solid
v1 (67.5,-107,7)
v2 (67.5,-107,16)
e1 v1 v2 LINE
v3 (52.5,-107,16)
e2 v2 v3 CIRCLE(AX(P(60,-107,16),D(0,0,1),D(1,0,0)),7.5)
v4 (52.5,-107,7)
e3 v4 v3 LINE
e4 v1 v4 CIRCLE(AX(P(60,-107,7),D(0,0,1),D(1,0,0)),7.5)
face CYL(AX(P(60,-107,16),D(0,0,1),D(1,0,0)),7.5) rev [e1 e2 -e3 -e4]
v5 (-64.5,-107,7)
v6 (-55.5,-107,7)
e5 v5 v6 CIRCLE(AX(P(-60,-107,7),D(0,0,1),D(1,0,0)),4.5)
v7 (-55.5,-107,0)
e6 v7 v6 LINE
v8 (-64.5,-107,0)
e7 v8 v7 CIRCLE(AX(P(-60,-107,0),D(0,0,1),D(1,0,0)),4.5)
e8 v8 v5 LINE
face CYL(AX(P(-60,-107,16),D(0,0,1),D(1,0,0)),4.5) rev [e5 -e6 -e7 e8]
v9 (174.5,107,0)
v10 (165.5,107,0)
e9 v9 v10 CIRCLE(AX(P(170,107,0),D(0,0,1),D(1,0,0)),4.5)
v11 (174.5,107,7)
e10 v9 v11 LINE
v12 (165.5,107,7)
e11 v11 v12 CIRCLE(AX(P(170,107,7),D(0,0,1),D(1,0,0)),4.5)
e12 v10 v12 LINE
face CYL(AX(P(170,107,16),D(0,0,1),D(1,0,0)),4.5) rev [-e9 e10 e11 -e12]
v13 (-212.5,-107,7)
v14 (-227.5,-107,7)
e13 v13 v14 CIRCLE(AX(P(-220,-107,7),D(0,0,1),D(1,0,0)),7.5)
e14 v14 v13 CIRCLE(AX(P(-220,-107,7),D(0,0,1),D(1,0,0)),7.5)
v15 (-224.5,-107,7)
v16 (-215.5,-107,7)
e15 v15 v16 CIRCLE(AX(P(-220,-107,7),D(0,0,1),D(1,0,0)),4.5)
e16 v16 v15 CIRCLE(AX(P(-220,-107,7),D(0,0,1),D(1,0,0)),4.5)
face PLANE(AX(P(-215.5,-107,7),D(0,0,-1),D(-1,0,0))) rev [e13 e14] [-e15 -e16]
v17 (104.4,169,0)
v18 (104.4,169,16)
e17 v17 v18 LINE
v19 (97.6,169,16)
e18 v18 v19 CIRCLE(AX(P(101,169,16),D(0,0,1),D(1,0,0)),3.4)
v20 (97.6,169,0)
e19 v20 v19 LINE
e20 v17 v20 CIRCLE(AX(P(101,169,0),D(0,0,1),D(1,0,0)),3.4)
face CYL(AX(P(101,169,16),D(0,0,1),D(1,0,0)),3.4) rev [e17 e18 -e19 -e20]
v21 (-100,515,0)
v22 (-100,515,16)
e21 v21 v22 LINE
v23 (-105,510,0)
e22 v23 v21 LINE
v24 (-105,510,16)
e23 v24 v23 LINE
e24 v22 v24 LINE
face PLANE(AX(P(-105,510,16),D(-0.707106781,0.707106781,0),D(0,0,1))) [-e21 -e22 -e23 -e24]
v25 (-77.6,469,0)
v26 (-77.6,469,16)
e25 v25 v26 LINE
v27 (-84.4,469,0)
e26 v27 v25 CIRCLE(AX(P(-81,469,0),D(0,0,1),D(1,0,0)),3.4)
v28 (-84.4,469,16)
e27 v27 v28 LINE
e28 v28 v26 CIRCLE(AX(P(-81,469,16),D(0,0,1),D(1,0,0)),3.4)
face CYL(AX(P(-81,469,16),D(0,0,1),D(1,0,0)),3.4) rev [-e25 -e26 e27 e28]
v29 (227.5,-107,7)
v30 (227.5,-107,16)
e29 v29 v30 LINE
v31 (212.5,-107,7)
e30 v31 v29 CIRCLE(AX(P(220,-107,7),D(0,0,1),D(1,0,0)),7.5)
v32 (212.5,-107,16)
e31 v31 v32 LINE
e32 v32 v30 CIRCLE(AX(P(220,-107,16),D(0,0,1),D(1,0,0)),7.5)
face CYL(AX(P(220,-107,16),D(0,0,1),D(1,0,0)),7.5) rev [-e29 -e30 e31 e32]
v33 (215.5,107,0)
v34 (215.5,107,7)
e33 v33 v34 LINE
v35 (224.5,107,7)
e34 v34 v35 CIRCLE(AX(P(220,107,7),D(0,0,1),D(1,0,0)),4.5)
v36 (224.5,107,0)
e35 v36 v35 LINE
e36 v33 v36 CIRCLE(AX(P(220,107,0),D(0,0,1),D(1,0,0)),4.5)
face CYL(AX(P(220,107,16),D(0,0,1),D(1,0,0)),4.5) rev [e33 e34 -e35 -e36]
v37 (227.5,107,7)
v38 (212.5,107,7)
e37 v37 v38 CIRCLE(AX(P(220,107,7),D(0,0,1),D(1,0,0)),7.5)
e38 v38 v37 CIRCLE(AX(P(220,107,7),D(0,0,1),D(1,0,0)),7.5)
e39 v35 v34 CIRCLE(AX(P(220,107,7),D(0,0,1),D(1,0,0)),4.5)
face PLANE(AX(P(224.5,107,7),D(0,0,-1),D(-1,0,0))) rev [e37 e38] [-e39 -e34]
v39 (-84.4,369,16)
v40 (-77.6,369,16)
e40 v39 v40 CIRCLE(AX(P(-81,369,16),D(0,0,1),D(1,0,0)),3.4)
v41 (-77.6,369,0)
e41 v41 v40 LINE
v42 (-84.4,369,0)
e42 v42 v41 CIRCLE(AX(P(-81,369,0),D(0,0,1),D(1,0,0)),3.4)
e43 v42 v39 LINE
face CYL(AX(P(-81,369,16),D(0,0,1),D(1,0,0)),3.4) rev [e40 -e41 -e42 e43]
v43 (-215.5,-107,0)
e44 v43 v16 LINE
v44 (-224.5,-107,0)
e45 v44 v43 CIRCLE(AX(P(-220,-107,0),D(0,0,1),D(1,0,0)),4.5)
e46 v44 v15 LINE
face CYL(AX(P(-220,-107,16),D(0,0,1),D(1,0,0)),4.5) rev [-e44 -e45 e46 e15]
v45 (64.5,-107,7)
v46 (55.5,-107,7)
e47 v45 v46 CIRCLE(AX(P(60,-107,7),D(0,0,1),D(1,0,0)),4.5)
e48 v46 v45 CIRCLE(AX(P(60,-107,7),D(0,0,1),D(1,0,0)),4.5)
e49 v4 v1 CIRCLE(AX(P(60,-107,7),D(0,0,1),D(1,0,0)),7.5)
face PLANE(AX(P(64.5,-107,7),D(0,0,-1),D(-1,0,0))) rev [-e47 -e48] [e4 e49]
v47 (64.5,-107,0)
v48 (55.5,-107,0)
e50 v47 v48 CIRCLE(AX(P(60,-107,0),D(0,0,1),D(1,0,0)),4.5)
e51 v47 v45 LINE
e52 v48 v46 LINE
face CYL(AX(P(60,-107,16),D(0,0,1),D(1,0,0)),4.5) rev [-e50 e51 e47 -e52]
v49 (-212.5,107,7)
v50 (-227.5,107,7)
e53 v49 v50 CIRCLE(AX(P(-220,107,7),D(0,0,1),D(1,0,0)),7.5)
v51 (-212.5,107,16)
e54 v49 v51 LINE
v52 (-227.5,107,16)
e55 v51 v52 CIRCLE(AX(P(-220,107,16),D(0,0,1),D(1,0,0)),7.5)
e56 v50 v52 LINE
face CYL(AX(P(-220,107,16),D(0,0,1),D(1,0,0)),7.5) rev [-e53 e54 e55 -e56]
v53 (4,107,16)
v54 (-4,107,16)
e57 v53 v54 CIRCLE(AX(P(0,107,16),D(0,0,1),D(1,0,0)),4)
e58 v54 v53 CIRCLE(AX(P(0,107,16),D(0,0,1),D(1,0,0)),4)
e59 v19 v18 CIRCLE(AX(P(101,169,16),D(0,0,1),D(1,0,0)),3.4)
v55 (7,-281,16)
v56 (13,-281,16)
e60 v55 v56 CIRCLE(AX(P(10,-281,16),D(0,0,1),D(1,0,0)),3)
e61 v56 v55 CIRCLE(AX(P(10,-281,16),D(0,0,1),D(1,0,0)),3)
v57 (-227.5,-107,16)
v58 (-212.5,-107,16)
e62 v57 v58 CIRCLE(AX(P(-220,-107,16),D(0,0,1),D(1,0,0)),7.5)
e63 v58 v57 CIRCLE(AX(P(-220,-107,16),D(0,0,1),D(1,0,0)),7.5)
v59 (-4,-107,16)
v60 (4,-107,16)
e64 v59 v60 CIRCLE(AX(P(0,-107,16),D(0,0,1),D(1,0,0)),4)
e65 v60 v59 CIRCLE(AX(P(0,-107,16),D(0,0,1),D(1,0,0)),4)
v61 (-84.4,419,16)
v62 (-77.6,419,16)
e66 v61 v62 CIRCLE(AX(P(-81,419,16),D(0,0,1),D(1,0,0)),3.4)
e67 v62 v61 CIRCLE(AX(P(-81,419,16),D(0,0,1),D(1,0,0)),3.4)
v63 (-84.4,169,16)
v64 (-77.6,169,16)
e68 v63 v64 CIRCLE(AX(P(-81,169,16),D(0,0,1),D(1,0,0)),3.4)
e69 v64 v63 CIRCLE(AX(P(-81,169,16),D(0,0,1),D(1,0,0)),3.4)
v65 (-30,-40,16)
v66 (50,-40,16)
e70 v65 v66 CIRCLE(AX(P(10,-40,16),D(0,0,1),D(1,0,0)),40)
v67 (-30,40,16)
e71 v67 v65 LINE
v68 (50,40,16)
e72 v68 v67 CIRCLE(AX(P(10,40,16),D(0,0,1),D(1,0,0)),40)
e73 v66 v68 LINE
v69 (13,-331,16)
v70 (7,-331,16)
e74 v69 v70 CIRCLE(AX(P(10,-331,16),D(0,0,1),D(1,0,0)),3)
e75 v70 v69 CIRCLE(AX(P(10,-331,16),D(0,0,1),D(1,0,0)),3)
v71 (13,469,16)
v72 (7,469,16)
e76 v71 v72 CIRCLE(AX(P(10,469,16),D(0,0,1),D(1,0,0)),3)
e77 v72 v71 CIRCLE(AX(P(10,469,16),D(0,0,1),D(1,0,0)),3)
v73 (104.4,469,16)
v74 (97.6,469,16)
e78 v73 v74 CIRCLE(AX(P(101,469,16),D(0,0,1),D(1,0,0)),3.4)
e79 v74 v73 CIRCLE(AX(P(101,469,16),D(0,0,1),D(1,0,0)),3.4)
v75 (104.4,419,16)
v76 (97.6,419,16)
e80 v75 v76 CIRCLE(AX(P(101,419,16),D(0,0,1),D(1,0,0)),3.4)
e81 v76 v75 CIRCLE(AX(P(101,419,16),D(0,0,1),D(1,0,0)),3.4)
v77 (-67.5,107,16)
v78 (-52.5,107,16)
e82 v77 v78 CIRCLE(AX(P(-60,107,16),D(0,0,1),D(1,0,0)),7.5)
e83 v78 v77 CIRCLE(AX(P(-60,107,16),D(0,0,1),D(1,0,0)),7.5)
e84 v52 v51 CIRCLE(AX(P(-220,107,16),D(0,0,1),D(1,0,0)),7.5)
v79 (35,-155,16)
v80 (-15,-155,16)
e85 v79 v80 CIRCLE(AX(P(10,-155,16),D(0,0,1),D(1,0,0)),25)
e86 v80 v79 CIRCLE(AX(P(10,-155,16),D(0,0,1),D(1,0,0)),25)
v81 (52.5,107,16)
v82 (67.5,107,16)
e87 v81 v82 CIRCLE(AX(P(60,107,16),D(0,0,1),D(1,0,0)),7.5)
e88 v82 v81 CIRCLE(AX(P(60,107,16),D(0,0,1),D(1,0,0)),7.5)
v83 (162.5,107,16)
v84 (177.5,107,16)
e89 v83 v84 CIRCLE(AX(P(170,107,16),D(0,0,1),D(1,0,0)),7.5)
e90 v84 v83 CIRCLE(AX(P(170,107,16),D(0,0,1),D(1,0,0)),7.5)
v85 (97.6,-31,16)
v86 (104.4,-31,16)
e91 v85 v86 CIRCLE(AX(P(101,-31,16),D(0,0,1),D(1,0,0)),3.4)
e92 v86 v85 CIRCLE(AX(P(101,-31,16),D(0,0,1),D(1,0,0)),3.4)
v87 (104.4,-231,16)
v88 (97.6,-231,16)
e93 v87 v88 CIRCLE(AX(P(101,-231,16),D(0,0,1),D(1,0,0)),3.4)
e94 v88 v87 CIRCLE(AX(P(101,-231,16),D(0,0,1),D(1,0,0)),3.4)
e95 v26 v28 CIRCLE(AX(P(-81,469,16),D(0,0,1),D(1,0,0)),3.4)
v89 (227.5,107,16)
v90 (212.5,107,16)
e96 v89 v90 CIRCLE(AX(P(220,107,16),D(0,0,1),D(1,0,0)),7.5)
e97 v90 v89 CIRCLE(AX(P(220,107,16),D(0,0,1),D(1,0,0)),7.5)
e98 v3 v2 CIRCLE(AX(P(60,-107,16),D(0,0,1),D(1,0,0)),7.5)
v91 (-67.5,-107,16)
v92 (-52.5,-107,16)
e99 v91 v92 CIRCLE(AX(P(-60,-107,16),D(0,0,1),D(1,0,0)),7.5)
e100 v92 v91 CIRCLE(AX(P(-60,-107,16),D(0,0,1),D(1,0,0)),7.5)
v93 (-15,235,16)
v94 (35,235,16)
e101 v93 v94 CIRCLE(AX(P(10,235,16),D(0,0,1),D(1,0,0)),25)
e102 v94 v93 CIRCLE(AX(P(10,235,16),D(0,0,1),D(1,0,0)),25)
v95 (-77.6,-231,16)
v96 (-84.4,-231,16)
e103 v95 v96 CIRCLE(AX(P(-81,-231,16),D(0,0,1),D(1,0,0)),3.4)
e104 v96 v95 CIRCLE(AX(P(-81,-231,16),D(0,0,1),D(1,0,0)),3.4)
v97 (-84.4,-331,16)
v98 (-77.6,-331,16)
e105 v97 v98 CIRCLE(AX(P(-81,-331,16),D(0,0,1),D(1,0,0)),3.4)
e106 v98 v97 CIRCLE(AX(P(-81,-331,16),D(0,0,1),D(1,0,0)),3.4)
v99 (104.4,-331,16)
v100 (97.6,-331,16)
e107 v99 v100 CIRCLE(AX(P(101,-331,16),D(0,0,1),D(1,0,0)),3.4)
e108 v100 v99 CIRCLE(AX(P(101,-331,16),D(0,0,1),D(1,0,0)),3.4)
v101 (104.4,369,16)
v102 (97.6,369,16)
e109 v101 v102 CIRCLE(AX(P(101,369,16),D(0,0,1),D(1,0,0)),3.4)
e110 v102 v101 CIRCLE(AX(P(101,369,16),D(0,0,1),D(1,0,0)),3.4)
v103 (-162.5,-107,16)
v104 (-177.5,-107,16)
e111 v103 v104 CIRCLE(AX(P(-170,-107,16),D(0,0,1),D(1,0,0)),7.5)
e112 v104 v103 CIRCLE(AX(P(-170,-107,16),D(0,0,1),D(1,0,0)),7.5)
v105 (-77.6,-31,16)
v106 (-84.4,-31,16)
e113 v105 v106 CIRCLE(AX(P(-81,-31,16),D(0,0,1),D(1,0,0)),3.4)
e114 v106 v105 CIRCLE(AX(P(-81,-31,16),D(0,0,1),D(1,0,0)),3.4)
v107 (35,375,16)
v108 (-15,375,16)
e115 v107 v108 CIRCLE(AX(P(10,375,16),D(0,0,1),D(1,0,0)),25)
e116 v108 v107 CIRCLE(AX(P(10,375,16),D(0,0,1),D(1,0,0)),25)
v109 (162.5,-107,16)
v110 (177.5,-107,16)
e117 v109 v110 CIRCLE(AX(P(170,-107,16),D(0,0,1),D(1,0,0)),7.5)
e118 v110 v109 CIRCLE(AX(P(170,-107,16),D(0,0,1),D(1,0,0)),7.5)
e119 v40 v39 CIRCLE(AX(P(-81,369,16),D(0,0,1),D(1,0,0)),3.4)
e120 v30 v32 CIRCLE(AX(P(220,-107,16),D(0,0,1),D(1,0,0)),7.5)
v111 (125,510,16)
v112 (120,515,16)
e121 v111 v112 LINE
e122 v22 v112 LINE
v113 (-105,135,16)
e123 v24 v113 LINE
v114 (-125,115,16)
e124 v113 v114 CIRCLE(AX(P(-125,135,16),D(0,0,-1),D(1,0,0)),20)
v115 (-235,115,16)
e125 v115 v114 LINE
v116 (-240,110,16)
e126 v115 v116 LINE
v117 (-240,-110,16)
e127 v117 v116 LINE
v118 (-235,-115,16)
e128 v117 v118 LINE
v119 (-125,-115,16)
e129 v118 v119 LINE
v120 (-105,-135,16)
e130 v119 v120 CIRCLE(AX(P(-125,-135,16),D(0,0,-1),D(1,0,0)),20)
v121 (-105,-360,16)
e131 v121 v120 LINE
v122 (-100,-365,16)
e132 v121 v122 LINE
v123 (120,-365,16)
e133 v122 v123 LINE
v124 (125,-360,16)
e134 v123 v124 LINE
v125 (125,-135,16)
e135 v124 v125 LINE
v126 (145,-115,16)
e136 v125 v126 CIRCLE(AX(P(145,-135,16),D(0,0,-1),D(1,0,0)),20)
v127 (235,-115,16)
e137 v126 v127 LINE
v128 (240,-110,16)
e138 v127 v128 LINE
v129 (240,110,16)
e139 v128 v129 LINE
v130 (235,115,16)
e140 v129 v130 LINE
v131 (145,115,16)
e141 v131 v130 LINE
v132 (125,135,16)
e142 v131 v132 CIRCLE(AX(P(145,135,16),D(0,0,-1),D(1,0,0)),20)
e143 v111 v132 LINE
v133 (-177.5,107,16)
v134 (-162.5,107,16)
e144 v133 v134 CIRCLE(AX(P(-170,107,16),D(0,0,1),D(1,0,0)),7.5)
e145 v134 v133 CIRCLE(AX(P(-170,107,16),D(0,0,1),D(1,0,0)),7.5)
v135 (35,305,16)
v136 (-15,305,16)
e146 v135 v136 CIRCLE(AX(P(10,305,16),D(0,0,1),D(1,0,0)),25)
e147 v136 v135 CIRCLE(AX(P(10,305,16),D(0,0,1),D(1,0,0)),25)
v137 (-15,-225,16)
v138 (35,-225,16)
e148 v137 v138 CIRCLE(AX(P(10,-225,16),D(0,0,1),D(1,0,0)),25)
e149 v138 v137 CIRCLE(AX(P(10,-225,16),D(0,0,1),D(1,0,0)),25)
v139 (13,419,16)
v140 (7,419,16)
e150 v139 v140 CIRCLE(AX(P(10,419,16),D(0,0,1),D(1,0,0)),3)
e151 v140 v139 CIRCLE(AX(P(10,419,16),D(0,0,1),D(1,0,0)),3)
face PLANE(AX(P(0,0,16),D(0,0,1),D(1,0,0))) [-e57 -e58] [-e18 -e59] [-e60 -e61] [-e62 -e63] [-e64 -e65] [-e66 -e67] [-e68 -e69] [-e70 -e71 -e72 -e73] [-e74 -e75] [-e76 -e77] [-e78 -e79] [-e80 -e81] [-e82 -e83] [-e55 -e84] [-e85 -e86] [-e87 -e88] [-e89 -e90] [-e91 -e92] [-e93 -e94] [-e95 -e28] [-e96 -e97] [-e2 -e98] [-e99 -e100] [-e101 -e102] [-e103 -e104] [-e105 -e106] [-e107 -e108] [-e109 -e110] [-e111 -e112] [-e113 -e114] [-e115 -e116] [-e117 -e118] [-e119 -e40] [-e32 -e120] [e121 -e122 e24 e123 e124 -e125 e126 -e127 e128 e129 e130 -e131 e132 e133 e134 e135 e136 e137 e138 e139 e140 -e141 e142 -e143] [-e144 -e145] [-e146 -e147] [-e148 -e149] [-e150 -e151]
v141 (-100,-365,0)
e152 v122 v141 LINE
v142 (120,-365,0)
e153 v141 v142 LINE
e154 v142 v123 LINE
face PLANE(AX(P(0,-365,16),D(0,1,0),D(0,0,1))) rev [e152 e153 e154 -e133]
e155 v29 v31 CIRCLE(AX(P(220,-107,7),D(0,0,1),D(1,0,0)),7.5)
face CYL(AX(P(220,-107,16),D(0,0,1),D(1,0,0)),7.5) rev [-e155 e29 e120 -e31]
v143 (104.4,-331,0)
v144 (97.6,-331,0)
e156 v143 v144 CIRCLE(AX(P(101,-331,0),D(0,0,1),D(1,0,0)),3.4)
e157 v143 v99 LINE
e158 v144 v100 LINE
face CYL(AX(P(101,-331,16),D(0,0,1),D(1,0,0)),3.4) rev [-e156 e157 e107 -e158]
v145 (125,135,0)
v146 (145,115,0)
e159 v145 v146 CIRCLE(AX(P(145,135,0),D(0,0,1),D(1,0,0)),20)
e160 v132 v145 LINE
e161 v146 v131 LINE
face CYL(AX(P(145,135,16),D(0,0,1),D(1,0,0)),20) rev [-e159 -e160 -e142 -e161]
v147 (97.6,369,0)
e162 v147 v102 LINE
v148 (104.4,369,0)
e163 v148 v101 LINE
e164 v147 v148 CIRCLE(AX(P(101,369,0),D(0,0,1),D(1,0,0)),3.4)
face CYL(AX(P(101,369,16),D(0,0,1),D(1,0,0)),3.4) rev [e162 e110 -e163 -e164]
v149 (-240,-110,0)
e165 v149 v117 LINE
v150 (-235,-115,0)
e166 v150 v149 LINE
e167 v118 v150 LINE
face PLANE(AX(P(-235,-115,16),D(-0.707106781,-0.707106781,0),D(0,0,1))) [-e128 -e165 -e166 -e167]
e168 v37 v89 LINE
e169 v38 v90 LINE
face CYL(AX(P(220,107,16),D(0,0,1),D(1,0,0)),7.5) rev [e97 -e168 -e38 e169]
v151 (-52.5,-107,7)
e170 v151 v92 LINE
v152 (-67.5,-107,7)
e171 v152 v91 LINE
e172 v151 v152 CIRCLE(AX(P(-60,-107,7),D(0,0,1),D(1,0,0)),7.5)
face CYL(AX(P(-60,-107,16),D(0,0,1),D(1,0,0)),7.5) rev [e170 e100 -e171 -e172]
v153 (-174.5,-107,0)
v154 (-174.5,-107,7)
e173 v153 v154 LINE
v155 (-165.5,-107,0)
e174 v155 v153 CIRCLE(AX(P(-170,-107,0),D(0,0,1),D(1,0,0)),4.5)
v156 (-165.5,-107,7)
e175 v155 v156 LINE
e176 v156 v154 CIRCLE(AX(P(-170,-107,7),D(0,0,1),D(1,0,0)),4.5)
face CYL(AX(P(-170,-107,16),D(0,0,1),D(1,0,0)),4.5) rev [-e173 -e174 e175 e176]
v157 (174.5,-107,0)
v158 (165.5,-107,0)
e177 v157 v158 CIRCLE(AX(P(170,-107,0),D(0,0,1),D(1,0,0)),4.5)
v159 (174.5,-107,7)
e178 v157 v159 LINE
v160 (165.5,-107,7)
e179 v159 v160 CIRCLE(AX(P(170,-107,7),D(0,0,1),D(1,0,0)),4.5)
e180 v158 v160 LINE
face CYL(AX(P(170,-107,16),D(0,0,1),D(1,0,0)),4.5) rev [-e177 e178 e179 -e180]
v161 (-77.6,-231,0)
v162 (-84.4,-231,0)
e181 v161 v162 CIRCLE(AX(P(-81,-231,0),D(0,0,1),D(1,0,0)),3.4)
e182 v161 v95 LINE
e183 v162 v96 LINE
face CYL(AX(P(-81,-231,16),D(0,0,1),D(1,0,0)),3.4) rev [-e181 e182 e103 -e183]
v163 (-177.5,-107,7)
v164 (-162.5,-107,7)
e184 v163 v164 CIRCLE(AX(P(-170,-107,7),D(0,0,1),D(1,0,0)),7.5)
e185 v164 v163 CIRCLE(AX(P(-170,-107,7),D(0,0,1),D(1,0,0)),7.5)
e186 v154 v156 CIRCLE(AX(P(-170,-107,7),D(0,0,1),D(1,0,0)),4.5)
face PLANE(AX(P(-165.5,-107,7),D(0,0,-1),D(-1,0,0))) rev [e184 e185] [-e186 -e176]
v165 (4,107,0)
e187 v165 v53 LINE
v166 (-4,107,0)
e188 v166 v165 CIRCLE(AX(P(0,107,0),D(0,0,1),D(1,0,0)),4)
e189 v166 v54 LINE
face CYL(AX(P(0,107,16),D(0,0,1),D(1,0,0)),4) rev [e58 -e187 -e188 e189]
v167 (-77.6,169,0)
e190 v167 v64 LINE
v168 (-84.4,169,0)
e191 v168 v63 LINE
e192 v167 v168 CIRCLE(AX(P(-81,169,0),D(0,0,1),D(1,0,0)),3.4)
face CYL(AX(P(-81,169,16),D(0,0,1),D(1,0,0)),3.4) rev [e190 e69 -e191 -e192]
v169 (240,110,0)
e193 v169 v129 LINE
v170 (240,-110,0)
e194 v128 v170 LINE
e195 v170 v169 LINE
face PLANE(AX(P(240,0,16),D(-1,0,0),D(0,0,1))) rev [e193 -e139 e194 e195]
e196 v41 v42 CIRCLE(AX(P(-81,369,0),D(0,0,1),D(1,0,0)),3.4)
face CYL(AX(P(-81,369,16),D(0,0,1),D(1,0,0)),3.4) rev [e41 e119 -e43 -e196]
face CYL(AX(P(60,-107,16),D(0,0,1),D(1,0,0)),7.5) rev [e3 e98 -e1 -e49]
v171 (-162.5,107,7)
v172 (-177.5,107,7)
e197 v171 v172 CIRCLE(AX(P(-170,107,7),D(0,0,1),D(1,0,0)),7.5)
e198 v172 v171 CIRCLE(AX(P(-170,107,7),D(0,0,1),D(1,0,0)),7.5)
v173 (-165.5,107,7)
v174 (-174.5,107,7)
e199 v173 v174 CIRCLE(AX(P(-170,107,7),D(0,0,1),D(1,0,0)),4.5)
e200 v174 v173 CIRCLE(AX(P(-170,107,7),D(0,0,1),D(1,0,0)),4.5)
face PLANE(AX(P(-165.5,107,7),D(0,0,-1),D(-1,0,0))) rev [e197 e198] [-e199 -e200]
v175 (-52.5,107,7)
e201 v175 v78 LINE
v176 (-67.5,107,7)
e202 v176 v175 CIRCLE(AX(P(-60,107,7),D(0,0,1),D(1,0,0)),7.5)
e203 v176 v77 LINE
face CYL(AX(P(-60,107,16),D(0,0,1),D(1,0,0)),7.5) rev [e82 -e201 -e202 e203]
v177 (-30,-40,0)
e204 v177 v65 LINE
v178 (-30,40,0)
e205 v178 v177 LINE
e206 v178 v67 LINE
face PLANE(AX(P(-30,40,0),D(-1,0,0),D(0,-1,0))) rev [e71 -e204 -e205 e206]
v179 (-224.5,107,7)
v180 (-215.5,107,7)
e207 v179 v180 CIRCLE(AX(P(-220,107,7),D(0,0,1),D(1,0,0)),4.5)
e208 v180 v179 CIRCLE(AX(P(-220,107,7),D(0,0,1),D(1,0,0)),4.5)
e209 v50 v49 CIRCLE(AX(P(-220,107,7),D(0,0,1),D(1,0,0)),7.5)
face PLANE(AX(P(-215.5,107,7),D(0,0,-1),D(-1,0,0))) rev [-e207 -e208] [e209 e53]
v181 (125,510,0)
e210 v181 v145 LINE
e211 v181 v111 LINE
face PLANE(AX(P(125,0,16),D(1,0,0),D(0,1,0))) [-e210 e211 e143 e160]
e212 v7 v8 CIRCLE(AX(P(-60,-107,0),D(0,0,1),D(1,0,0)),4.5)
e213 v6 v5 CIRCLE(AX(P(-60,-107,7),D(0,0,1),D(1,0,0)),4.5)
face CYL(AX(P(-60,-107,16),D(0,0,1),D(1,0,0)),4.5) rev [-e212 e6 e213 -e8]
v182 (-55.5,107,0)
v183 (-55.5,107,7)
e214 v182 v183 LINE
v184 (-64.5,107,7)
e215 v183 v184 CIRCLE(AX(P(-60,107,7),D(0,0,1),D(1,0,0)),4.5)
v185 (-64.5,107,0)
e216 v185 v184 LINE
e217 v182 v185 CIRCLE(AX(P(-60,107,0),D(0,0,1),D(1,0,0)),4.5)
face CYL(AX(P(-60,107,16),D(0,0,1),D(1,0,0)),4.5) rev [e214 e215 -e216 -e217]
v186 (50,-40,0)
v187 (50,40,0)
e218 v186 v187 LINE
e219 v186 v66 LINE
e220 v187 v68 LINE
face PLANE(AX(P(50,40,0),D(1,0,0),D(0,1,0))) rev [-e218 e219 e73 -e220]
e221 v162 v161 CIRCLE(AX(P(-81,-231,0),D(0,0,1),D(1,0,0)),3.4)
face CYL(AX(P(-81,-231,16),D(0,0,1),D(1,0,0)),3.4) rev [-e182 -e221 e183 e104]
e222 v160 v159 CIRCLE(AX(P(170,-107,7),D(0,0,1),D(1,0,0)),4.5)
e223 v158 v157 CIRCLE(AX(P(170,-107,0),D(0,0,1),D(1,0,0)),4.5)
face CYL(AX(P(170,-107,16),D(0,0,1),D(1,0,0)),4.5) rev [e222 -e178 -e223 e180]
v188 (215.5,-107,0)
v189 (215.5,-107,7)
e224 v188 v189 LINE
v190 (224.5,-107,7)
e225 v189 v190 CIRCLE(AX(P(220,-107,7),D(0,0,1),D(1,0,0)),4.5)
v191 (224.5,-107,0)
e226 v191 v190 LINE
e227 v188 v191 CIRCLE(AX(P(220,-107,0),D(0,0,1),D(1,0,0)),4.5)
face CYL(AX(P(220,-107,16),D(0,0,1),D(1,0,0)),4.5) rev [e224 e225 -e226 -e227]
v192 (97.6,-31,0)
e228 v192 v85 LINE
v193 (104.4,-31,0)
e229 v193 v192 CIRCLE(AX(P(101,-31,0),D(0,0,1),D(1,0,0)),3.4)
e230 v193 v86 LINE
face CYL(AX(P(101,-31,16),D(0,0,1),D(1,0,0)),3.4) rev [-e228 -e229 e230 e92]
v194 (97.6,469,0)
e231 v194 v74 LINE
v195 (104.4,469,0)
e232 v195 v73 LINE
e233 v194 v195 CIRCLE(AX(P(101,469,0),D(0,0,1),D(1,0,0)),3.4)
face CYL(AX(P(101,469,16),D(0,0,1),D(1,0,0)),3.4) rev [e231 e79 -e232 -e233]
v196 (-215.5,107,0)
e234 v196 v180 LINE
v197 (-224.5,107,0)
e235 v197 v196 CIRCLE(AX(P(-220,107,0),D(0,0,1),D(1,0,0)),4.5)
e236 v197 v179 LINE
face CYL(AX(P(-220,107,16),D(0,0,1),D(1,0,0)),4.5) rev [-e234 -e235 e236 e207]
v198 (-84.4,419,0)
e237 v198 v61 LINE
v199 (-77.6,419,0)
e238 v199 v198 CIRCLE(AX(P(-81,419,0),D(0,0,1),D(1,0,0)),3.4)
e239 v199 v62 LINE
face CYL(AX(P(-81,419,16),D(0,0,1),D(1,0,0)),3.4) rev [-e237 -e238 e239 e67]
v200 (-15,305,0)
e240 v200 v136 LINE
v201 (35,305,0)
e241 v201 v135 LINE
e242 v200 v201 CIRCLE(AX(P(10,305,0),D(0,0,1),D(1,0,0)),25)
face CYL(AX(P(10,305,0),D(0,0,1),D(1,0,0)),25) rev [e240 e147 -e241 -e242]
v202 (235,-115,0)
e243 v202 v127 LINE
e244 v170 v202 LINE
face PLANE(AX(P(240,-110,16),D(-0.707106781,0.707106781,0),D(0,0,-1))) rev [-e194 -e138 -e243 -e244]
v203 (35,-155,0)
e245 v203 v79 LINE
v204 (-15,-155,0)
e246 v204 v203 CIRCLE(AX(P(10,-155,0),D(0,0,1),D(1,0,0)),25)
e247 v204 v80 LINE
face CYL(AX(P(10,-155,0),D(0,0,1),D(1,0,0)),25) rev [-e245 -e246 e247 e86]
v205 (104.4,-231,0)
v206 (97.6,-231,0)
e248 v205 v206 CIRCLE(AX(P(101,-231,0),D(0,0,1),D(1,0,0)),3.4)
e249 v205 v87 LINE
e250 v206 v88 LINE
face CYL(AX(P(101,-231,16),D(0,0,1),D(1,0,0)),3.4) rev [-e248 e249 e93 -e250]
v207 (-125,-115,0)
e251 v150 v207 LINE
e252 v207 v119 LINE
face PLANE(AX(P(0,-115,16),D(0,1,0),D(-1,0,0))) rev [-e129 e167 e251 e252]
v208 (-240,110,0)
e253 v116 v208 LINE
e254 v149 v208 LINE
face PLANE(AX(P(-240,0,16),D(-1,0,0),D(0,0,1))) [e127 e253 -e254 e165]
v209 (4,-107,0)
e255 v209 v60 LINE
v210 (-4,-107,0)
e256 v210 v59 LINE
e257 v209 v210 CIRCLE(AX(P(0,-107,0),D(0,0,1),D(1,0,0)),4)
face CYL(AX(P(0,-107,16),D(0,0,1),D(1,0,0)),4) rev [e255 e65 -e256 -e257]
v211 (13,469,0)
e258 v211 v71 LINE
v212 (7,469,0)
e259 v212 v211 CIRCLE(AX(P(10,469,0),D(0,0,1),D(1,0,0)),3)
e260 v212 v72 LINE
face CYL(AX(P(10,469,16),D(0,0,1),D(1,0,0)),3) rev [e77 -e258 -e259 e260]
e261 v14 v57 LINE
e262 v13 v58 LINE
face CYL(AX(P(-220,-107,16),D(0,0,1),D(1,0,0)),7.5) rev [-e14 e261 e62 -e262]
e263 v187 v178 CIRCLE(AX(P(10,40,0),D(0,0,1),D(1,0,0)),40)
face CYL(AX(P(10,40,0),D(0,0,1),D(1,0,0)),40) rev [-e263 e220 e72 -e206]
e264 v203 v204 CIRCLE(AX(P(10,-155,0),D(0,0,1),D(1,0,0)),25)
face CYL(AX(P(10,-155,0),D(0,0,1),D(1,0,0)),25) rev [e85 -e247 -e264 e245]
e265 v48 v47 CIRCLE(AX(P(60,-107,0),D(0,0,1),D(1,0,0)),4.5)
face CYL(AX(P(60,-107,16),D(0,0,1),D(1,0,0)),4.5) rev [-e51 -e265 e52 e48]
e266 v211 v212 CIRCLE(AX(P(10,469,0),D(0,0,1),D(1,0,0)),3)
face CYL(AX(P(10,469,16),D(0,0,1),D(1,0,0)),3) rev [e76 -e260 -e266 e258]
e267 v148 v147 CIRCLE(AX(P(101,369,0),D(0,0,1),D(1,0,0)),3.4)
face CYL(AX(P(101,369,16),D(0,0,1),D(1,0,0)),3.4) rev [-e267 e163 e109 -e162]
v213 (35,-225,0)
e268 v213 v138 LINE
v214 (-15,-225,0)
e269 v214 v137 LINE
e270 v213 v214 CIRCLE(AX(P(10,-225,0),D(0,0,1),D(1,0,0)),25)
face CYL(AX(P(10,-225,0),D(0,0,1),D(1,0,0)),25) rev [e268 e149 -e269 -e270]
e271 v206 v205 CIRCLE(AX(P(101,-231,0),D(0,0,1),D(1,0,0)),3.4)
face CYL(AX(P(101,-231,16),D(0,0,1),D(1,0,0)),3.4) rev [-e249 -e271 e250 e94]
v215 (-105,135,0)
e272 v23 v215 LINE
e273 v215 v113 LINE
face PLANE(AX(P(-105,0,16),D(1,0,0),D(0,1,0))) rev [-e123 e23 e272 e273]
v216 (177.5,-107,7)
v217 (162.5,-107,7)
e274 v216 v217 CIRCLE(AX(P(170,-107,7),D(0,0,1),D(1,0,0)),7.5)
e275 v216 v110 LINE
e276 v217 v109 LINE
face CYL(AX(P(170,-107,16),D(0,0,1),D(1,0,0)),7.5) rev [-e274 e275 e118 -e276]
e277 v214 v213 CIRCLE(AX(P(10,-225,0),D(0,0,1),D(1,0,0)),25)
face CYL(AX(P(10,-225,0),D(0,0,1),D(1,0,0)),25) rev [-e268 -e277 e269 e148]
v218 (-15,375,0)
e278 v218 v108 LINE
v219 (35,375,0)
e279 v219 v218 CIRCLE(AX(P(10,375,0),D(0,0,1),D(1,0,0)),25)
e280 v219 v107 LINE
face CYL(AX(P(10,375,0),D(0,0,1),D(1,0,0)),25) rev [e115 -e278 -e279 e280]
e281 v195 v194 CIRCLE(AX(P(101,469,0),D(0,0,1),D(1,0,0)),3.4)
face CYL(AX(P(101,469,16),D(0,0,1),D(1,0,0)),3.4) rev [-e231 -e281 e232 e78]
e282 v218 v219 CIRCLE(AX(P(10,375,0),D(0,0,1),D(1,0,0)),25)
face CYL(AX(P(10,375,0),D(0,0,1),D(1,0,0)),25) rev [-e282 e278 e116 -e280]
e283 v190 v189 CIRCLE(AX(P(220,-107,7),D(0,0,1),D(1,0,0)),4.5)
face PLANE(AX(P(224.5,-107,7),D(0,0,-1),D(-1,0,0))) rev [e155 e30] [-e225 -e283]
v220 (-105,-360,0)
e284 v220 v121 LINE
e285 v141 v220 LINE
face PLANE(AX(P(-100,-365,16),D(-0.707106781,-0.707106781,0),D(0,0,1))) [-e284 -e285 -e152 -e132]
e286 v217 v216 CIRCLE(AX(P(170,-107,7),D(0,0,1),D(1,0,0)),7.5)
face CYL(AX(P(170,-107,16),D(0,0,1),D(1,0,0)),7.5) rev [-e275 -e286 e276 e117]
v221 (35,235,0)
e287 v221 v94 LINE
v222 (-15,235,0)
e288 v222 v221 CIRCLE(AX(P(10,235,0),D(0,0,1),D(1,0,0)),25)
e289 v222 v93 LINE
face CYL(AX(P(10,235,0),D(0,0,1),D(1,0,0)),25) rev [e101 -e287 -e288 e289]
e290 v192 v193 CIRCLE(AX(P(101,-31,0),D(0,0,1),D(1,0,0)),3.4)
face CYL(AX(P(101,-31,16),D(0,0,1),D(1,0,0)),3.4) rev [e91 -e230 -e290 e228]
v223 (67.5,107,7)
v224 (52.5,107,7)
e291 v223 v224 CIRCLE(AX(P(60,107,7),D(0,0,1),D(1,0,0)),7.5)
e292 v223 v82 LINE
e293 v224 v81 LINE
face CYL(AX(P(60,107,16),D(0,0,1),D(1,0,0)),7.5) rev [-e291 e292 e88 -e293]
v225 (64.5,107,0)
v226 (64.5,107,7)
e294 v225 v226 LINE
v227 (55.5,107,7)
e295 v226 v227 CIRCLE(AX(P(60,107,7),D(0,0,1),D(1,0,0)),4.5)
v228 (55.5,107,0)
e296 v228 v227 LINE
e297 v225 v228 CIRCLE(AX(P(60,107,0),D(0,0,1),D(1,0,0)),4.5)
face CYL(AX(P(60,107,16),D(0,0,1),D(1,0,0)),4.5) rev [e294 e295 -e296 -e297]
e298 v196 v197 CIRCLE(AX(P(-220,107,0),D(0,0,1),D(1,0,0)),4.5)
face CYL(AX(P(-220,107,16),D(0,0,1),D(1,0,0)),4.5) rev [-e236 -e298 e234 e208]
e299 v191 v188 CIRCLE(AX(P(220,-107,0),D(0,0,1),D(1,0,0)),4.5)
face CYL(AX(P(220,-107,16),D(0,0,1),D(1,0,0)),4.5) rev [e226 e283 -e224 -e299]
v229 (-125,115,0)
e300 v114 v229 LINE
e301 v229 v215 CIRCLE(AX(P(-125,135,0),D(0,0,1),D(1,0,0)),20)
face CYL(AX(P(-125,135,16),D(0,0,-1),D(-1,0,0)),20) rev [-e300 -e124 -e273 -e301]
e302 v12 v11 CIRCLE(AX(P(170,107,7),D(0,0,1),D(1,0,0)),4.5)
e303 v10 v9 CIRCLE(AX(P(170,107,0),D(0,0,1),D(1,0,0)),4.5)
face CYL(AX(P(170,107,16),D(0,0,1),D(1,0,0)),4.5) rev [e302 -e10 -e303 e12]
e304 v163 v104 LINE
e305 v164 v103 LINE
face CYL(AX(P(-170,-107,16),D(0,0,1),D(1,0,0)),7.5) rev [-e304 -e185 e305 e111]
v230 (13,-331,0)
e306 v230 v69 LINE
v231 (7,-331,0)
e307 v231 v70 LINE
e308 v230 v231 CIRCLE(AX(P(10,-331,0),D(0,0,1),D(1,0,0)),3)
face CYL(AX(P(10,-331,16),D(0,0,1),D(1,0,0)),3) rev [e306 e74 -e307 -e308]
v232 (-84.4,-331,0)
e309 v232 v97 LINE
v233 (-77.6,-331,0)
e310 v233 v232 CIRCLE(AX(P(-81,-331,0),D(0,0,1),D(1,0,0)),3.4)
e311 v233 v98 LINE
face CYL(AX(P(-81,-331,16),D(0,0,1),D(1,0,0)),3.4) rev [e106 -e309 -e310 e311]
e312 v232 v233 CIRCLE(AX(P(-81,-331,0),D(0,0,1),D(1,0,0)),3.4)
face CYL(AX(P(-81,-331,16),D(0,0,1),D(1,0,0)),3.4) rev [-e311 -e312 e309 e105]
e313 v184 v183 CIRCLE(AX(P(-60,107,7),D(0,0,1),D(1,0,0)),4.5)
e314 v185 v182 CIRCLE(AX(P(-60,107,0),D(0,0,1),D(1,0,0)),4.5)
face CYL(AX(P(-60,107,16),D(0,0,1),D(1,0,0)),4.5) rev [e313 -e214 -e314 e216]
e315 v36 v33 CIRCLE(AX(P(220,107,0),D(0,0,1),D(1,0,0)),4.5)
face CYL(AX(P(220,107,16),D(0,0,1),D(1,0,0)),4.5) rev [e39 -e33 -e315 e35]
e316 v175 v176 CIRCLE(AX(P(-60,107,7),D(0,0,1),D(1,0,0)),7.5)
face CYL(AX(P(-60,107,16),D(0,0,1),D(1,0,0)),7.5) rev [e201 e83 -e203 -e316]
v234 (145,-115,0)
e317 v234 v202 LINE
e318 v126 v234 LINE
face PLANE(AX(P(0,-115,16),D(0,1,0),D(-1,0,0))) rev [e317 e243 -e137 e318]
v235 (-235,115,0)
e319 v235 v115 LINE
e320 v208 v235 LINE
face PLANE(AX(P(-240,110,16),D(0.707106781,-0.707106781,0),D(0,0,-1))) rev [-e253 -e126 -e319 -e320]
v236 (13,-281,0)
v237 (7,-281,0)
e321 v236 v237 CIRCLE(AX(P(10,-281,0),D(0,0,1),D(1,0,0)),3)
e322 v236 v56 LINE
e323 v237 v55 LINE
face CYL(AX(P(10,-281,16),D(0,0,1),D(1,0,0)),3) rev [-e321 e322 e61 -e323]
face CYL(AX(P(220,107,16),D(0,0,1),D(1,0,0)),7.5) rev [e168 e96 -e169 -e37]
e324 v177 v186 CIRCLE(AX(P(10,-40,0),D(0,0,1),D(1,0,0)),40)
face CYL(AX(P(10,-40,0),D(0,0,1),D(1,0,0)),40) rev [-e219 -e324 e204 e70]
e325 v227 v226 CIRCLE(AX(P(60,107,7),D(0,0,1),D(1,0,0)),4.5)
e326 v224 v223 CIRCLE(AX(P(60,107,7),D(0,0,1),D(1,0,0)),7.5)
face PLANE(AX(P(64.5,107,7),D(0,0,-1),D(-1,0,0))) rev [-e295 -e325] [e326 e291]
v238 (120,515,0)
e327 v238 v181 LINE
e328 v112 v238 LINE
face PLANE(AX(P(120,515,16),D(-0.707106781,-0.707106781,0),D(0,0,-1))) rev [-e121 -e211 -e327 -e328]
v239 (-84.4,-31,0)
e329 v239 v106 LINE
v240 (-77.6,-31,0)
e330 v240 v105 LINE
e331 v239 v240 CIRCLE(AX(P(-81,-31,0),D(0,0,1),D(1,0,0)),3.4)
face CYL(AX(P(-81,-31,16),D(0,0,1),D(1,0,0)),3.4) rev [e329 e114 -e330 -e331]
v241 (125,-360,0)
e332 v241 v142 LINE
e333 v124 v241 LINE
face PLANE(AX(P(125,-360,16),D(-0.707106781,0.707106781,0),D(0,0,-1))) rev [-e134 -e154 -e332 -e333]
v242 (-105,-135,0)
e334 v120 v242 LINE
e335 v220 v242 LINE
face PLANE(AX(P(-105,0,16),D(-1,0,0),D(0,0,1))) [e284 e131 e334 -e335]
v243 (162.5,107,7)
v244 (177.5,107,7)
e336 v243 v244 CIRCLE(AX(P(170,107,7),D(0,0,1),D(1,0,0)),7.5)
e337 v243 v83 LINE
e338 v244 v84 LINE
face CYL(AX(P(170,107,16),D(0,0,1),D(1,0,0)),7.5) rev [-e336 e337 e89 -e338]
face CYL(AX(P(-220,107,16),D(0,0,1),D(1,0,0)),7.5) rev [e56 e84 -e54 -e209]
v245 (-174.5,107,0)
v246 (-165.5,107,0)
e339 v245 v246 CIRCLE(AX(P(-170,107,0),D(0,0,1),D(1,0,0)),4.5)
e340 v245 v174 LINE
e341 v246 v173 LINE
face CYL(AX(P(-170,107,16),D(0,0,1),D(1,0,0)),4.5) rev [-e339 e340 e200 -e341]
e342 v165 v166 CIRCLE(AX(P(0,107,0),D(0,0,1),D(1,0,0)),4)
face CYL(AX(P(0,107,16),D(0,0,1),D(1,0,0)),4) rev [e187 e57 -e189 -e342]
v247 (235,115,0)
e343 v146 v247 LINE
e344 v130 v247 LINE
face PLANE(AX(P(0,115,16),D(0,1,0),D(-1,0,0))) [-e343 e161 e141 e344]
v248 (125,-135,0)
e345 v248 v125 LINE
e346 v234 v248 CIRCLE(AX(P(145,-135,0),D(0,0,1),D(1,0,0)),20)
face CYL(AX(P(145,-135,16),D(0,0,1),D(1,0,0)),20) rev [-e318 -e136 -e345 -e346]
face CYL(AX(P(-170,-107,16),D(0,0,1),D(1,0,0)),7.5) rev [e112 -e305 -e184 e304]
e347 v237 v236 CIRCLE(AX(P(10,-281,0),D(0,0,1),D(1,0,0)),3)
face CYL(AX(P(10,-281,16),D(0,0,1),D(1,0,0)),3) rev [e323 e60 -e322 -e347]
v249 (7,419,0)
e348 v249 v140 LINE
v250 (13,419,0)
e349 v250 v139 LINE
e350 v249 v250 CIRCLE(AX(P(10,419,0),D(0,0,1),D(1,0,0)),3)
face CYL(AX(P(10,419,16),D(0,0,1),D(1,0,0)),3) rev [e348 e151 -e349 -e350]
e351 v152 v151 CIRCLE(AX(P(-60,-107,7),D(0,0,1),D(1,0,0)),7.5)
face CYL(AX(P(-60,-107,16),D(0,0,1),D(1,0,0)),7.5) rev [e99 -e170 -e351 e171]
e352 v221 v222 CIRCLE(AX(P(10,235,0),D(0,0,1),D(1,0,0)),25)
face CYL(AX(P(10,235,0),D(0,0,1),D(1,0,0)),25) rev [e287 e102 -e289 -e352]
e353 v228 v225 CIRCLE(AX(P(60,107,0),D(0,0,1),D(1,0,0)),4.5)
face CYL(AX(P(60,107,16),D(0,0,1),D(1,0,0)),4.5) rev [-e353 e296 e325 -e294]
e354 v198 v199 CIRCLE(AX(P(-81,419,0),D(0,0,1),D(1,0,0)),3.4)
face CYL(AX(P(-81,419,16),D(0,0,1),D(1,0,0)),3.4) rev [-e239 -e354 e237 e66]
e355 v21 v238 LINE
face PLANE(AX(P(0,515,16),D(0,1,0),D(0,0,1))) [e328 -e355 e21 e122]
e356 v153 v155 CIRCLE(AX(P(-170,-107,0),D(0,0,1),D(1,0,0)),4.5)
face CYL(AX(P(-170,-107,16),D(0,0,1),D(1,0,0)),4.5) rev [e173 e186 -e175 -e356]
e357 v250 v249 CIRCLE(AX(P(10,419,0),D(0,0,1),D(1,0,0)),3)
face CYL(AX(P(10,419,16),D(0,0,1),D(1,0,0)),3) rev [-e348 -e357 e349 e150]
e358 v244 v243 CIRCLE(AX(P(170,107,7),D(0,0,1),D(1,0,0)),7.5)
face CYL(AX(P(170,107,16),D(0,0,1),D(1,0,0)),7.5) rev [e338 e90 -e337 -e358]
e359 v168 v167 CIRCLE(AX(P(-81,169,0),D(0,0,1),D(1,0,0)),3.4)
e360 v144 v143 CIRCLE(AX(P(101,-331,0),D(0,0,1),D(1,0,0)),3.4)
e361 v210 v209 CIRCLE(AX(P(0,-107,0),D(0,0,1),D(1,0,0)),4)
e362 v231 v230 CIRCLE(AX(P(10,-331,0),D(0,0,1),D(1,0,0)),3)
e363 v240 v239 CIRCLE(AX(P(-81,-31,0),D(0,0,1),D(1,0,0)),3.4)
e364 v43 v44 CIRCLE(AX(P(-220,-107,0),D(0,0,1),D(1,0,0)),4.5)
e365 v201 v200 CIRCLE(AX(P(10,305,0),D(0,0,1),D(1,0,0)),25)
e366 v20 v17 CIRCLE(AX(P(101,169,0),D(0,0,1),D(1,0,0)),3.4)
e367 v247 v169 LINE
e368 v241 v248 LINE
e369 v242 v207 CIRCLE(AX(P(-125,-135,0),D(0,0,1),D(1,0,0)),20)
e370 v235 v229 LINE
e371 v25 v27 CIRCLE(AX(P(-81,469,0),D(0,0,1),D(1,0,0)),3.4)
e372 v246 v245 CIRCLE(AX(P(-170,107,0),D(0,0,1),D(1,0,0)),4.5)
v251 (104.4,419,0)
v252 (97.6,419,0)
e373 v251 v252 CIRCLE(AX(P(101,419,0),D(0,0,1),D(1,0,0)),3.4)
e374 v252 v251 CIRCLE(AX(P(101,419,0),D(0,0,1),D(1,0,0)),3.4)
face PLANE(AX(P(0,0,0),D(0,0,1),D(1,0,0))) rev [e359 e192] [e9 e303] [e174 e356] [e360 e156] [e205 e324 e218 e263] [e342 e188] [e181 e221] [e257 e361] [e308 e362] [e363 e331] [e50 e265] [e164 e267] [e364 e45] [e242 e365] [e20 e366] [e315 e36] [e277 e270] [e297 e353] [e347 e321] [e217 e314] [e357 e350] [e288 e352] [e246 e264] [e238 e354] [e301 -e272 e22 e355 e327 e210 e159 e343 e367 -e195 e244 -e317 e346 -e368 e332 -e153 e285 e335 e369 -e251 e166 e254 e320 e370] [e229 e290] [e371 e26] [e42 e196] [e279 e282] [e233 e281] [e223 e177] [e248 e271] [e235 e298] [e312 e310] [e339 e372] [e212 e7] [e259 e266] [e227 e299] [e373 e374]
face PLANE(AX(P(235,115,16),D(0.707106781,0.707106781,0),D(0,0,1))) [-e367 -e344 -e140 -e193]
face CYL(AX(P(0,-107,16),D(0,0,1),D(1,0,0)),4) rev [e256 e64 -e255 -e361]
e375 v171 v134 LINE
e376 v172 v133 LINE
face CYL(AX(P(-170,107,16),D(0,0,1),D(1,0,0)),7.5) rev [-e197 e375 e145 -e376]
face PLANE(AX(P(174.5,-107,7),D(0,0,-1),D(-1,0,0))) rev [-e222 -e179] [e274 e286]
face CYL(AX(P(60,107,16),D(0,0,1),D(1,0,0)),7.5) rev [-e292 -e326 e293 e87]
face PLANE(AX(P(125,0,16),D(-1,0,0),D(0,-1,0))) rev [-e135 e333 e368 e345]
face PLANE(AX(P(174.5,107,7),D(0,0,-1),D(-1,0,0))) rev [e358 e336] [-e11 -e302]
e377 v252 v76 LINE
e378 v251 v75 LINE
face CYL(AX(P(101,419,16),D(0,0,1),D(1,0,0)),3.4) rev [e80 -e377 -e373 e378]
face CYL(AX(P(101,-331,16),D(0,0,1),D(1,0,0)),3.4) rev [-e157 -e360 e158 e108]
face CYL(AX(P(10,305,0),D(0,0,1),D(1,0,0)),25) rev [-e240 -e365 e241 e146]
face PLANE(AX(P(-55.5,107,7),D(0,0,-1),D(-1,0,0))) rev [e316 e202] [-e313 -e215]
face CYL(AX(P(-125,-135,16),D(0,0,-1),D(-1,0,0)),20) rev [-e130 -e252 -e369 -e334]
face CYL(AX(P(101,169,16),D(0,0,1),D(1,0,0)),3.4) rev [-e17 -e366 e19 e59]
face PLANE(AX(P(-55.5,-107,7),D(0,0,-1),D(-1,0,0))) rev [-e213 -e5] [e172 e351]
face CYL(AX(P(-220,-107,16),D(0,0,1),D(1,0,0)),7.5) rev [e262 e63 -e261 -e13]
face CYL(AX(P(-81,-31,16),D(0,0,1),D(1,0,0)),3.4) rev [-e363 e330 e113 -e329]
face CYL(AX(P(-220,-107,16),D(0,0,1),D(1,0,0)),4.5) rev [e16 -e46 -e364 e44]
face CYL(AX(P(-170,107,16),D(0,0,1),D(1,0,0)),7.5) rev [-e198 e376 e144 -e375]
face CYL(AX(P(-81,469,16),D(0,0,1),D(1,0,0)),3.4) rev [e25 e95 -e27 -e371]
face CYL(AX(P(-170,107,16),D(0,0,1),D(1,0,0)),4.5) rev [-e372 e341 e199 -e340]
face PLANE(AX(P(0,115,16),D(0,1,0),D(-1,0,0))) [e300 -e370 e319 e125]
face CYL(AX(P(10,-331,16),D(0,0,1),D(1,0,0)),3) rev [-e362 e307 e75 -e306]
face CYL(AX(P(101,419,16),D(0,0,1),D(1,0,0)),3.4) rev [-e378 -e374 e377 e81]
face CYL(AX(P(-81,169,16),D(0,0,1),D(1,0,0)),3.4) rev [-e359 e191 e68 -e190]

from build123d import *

# Parameters (mm, degrees)
SKETCH_1_W                = 230
SKETCH_1_H                = 400
SKETCH_1_W_2              = 480
SKETCH_1_H_2              = 230
SKETCH_1_H_3              = 250
EXTRUDE_1_DEPTH           = 16
FILLET_1_R                = 20
HOLE_WIZARD_1_D           = 9
HOLE_WIZARD_1_CBORE_D     = 15
HOLE_WIZARD_1_CBORE_DEPTH = 9
MM_1_D                    = 8
HOLE_WIZARD_M8_1_D        = 6.8
HOLE_WIZARD_M8_1_DEPTH    = 22.25
HOLE_WIZARD_M8_1_TIP      = 2.042926105
CHAMFER_2_SIZE            = 5
CHAMFER_3_SIZE            = 5
SKETCH_8_R                = 25
CUT_EXTRUDE_1_DEPTH       = 569.402146372
MM_2_D                    = 6


with BuildPart() as part:
    # 草图1 → 凸台-拉伸1 (new body)
    with BuildSketch(Plane.XY):
        with Locations((10, 315)):
            Rectangle(SKETCH_1_W, SKETCH_1_H)
        Rectangle(SKETCH_1_W_2, SKETCH_1_H_2)
        with Locations((10, -240)):
            Rectangle(SKETCH_1_W, SKETCH_1_H_3)
    extrude(amount=EXTRUDE_1_DEPTH)

    # 圆角1
    fillet_1_edges = [part.edges().sort_by_distance(p)[0] for p in [
        (125, 115, 8),
        (125, -115, 8),
        (-105, -115, 8),
        (-105, 115, 8),
    ]]
    fillet(fillet_1_edges, radius=FILLET_1_R)

    # 打孔尺寸(%根据)内六角圆柱头螺钉的类型1 (through all)
    with Locations(Plane.XY.offset(16)):
        with Locations((60, -107), (220, 107), (-220, -107), (-220, 107), (220, -107), (-170, 107), (-170, -107), (170, 107), (170, -107), (-60, 107), (-60, -107), (60, 107)):
            CounterBoreHole(HOLE_WIZARD_1_D / 2, HOLE_WIZARD_1_CBORE_D / 2, HOLE_WIZARD_1_CBORE_DEPTH)

    # 大小mm 暗销孔1 (through all)
    with Locations(Plane.XY.offset(16)):
        with Locations((0, 107), (0, -107)):
            Hole(MM_1_D / 2)

    # M8 螺纹孔1
    with Locations(Plane.XY.offset(16)):
        with Locations((101, 469), (-81, 469), (-81, 169), (-81, 369), (-81, 419), (-81, -31), (-81, -231), (-81, -331), (101, -331), (101, -231), (101, -31), (101, 419), (101, 369), (101, 169)):
            Hole(HOLE_WIZARD_M8_1_D / 2, depth=HOLE_WIZARD_M8_1_DEPTH)
            with Locations((0, 0, -(HOLE_WIZARD_M8_1_DEPTH + HOLE_WIZARD_M8_1_TIP / 2))):  # 118° drill point
                Cone(0, HOLE_WIZARD_M8_1_D / 2, HOLE_WIZARD_M8_1_TIP, mode=Mode.SUBTRACT)

    # 倒角2
    chamfer_2_edges = [part.edges().sort_by_distance(p)[0] for p in [
        (125, -365, 8),
        (-105, -365, 8),
        (-105, 515, 8),
        (125, 515, 8),
    ]]
    chamfer(chamfer_2_edges, length=CHAMFER_2_SIZE)

    # 倒角3
    chamfer_3_edges = [part.edges().sort_by_distance(p)[0] for p in [
        (240, 115, 8),
        (240, -115, 8),
        (-240, -115, 8),
        (-240, 115, 8),
    ]]
    chamfer(chamfer_3_edges, length=CHAMFER_3_SIZE)

    # 草图8 → 切除-拉伸1 (cut, through all)
    with BuildSketch(Plane.XY.offset(16)):
        with Locations((10, 375)):
            Circle(SKETCH_8_R)
        with Locations((10, 305)):
            Circle(SKETCH_8_R)
        with Locations((10, -155)):
            Circle(SKETCH_8_R)
        with Locations((10, -225)):
            Circle(SKETCH_8_R)
        with Locations((10, 235)):
            Circle(SKETCH_8_R)
        with BuildLine():
            Line((50, 40), (50, -40))
            ThreePointArc((50, -40), (10, -80), (-30, -40))
            Line((-30, -40), (-30, 40))
            ThreePointArc((-30, 40), (10, 80), (50, 40))
        make_face()
    extrude(amount=-CUT_EXTRUDE_1_DEPTH, mode=Mode.SUBTRACT)

    # 大小mm 暗销孔2 (through all)
    with Locations(Plane.XY.offset(16)):
        with Locations((10, -281), (10, 469), (10, 419), (10, -331)):
            Hole(MM_2_D / 2)


solid = part.part
